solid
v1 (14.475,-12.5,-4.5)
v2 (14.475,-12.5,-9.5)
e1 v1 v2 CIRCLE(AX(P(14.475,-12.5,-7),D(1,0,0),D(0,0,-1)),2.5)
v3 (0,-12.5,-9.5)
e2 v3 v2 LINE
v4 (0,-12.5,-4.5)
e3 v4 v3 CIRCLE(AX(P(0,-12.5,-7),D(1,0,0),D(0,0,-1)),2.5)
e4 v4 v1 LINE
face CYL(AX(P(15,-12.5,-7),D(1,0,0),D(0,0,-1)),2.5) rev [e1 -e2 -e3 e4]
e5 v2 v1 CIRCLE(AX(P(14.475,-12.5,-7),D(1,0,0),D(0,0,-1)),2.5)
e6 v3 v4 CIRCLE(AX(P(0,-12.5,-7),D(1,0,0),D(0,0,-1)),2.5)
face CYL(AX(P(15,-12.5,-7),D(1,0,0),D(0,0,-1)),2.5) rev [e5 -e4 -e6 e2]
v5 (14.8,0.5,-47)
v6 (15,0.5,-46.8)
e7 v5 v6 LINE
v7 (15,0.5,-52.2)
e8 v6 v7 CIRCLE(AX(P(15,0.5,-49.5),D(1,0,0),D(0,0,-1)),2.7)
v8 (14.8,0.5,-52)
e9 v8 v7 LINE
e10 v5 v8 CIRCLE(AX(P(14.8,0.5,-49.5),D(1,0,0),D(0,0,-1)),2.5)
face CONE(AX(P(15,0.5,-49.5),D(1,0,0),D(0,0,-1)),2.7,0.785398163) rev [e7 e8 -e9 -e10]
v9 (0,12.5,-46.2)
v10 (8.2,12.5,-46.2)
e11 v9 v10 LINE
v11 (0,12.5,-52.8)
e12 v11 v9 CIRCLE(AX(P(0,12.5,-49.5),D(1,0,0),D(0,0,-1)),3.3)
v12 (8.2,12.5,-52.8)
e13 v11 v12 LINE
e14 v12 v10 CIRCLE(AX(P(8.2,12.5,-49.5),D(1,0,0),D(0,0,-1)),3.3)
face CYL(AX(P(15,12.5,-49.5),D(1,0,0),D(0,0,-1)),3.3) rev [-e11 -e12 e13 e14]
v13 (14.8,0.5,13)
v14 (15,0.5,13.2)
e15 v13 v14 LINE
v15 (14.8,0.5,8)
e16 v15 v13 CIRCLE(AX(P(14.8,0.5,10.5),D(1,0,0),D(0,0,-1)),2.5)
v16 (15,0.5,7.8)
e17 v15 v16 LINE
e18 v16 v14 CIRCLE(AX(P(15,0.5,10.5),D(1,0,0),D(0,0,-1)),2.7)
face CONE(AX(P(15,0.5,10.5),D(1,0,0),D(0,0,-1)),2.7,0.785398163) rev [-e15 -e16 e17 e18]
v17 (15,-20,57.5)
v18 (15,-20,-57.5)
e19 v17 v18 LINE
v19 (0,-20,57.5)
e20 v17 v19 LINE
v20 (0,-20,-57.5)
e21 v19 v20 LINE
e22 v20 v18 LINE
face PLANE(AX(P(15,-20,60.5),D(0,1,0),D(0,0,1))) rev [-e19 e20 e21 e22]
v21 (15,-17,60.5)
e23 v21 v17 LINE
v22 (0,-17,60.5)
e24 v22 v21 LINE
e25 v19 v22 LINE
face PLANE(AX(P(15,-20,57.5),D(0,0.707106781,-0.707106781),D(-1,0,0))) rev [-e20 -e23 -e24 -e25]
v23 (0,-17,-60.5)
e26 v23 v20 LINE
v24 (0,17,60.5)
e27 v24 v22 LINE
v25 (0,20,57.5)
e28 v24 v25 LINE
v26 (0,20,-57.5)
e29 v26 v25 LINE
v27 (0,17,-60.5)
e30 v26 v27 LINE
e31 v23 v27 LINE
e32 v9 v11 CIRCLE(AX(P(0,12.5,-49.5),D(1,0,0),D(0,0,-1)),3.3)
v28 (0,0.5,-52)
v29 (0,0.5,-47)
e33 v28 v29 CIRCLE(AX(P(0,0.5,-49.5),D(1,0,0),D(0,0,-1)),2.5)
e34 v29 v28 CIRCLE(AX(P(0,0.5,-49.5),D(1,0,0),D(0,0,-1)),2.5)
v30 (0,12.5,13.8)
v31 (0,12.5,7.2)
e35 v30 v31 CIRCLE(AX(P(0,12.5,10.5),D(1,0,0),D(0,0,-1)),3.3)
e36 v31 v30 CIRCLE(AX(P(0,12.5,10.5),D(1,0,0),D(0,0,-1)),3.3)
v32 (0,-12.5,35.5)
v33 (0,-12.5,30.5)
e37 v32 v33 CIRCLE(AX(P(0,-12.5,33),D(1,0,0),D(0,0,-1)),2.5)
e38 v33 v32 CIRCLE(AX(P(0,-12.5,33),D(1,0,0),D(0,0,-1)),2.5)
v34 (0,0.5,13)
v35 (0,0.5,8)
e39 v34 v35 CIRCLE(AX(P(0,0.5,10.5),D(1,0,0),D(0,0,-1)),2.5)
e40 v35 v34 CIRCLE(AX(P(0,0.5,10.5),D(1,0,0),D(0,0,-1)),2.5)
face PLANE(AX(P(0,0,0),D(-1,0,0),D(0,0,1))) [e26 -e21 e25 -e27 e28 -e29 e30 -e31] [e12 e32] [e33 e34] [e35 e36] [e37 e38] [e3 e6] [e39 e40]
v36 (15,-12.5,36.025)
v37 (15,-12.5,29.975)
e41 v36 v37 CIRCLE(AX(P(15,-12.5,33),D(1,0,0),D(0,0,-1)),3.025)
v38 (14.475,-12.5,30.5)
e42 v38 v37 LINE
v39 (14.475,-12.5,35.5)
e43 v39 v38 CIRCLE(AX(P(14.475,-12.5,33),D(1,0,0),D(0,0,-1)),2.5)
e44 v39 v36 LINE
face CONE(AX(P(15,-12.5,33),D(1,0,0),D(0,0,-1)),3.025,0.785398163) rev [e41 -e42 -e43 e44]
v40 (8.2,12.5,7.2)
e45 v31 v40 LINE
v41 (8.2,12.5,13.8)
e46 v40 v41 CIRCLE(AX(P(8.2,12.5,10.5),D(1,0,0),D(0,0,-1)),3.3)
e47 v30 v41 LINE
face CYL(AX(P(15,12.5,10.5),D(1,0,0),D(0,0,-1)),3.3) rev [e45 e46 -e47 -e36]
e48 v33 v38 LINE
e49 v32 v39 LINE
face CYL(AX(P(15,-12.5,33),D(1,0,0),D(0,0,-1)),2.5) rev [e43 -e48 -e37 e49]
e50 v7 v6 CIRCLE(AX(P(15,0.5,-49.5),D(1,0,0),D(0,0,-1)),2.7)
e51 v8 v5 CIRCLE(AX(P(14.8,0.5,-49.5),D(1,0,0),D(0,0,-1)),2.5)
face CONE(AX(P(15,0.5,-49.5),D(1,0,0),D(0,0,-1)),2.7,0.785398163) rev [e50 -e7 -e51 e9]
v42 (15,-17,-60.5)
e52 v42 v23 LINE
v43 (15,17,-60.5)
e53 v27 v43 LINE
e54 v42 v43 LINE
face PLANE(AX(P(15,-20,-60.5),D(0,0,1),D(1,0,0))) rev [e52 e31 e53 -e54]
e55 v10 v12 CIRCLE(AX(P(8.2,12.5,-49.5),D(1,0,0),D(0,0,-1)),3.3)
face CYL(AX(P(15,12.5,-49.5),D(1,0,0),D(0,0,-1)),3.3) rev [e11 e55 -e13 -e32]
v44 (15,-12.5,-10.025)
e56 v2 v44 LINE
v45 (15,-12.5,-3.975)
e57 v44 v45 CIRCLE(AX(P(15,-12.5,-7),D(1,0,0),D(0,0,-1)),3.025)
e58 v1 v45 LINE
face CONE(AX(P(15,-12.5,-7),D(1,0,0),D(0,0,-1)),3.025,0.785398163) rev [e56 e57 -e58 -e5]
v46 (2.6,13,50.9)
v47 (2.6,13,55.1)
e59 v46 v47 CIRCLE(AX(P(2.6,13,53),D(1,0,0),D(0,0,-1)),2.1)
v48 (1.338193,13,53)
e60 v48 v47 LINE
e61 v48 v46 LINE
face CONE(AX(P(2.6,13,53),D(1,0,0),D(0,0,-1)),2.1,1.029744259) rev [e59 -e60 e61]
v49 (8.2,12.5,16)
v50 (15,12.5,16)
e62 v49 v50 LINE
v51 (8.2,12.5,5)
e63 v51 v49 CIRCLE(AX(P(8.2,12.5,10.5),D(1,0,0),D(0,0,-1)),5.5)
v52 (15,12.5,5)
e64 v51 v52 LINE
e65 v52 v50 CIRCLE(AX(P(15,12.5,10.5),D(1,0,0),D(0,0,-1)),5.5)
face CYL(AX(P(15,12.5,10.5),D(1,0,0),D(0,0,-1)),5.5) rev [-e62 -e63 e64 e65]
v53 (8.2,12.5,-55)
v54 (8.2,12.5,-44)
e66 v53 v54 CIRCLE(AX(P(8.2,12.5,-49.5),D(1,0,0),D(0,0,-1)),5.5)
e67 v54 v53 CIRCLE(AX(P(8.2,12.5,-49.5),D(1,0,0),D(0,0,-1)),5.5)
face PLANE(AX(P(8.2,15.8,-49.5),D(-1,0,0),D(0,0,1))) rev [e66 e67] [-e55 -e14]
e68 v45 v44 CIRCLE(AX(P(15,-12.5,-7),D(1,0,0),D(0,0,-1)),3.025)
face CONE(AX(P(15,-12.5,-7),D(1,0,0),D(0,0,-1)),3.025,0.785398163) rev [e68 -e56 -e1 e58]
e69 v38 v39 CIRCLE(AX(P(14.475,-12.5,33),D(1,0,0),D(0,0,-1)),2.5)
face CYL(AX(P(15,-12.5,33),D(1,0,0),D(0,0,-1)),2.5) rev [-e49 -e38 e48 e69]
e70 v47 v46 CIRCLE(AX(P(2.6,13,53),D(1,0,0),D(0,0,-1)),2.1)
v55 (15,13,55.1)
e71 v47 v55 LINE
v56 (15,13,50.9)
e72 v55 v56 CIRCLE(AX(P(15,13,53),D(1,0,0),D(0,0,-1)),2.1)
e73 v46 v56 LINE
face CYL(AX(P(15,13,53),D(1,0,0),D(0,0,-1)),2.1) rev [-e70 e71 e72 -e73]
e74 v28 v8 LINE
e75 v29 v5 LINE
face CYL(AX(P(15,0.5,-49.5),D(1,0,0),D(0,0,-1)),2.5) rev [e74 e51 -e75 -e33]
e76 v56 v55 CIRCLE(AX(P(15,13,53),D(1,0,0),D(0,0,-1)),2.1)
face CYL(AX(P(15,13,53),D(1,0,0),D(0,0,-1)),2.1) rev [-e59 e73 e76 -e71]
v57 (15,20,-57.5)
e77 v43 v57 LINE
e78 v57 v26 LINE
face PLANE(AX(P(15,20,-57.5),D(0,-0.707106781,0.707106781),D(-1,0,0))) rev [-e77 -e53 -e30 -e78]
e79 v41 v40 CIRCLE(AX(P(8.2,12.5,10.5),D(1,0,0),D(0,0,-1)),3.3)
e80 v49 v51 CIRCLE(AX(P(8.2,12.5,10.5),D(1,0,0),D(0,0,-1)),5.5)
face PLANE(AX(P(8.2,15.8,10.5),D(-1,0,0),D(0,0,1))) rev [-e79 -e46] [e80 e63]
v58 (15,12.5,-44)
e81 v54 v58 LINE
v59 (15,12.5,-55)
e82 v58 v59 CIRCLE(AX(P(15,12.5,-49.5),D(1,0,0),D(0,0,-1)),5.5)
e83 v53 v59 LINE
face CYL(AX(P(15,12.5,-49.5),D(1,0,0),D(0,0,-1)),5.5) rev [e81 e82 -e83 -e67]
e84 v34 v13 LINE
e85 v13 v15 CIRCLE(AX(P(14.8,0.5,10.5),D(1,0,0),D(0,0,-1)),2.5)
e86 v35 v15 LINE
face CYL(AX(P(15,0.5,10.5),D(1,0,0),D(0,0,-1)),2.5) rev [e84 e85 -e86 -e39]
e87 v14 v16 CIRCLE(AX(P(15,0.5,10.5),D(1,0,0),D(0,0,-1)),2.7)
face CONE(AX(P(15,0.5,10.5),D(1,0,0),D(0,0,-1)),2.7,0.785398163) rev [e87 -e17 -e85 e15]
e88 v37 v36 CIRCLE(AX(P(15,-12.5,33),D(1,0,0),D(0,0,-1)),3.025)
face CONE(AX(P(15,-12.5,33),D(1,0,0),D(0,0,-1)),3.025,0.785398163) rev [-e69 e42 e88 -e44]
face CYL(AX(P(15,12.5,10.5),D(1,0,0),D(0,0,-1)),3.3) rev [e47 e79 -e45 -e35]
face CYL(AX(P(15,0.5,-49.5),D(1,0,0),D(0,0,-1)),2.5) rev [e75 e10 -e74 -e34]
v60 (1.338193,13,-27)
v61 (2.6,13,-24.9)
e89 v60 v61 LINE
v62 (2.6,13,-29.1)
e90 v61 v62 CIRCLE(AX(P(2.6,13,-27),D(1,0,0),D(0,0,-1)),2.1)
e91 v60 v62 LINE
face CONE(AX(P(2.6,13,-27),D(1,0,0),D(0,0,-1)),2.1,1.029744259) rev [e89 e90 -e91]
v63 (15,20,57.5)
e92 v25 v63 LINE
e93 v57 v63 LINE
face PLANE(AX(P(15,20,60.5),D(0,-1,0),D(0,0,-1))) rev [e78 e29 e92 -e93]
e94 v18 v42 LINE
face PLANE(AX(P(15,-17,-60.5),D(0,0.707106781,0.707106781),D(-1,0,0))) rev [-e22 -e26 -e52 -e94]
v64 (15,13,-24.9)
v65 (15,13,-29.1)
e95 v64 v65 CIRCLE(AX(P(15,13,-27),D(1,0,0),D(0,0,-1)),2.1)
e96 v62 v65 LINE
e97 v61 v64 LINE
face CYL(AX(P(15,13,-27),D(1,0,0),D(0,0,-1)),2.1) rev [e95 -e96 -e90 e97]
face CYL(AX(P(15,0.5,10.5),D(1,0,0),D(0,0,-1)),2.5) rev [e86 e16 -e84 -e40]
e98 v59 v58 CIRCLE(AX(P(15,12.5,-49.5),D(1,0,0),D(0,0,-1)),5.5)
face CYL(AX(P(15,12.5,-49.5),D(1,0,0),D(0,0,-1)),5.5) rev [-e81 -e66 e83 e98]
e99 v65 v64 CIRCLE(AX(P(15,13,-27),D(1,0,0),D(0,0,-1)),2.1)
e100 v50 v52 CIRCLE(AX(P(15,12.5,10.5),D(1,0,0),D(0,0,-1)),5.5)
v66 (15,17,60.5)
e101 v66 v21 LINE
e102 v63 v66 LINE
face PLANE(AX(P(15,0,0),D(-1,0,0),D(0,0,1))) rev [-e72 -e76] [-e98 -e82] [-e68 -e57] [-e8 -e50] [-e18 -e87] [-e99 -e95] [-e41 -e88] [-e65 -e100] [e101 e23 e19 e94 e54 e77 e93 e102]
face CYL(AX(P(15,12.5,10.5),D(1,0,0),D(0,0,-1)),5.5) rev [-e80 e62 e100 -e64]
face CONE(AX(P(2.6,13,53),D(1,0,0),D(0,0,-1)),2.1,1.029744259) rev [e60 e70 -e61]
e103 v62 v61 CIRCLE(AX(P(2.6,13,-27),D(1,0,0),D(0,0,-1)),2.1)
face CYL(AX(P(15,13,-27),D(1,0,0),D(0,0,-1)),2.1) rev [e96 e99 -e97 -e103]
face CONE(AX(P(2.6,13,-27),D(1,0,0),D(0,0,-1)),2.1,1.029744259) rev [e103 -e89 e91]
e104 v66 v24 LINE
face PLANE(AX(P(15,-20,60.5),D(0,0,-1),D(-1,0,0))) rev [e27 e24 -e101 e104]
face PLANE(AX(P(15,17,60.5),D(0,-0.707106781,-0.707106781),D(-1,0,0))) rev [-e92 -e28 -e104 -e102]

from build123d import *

# Parameters (mm, degrees)
SKETCH1_W                                            = 121
SKETCH1_H                                            = 40
BOSS_EXTRUDE1_DEPTH                                  = 15
M5_TAPPED_HOLE1_D                                    = 4.2
M5_TAPPED_HOLE1_DEPTH                                = 12.4
M5_TAPPED_HOLE1_TIP                                  = 1.2618073
M6_TAPPED_HOLE1_D                                    = 5
M6_TAPPED_HOLE1_DEPTH                                = 15
M6_TAPPED_HOLE1_CSINK_D                              = 6.05
M6_TAPPED_HOLE1_CSINK_ANGLE                          = 90
M6_TAPPED_HOLE1_TIP                                  = 1.502151548
CBORE_FOR_M6_HEXAGON_SOCKET_HEAD_CAP_SCR_D           = 6.6
CBORE_FOR_M6_HEXAGON_SOCKET_HEAD_CAP_SCR_CBORE_D     = 11
CBORE_FOR_M6_HEXAGON_SOCKET_HEAD_CAP_SCR_CBORE_DEPTH = 6.8
F_5_0MM_BLIND_HOLE_1_D                               = 5
F_5_0MM_BLIND_HOLE_1_CSINK_D                         = 5.4
F_5_0MM_BLIND_HOLE_1_CSINK_ANGLE                     = 90
CHAMFER1_SIZE                                        = 3


with BuildPart() as part:
    # Sketch1 → Boss-Extrude1 (new body)
    with BuildSketch(Plane(origin=(0, 0, 0), x_dir=(0, 0, -1), z_dir=(1, 0, 0))):
        Rectangle(SKETCH1_W, SKETCH1_H)
    extrude(amount=BOSS_EXTRUDE1_DEPTH)

    # M5 Tapped Hole1
    with Locations(Plane(origin=(15, 0, 0), x_dir=(0, 0, -1), z_dir=(1, 0, 0))):
        with Locations((-53, 13), (27, 13)):
            Hole(M5_TAPPED_HOLE1_D / 2, depth=M5_TAPPED_HOLE1_DEPTH)
            with Locations((0, 0, -(M5_TAPPED_HOLE1_DEPTH + M5_TAPPED_HOLE1_TIP / 2))):  # 118° drill point
                Cone(0, M5_TAPPED_HOLE1_D / 2, M5_TAPPED_HOLE1_TIP, mode=Mode.SUBTRACT)

    # M6 Tapped Hole1
    with Locations(Plane(origin=(15, 0, 0), x_dir=(0, 0, -1), z_dir=(1, 0, 0))):
        with Locations((-33, -12.5), (7, -12.5)):
            CounterSinkHole(M6_TAPPED_HOLE1_D / 2, M6_TAPPED_HOLE1_CSINK_D / 2, depth=M6_TAPPED_HOLE1_DEPTH, counter_sink_angle=M6_TAPPED_HOLE1_CSINK_ANGLE)
            with Locations((0, 0, -(M6_TAPPED_HOLE1_DEPTH + M6_TAPPED_HOLE1_TIP / 2))):  # 118° drill point
                Cone(0, M6_TAPPED_HOLE1_D / 2, M6_TAPPED_HOLE1_TIP, mode=Mode.SUBTRACT)

    # CBORE for M6 Hexagon socket head cap screws1 (through all)
    with Locations(Plane(origin=(15, 0, 0), x_dir=(0, 0, -1), z_dir=(1, 0, 0))):
        with Locations((-10.5, 12.5), (49.5, 12.5)):
            CounterBoreHole(CBORE_FOR_M6_HEXAGON_SOCKET_HEAD_CAP_SCR_D / 2, CBORE_FOR_M6_HEXAGON_SOCKET_HEAD_CAP_SCR_CBORE_D / 2, CBORE_FOR_M6_HEXAGON_SOCKET_HEAD_CAP_SCR_CBORE_DEPTH)

    # Ø5.0mm blind hole 1 (through all)
    with Locations(Plane(origin=(15, 0, 0), x_dir=(0, 0, -1), z_dir=(1, 0, 0))):
        with Locations((-10.5, 0.5), (49.5, 0.5)):
            CounterSinkHole(F_5_0MM_BLIND_HOLE_1_D / 2, F_5_0MM_BLIND_HOLE_1_CSINK_D / 2, counter_sink_angle=F_5_0MM_BLIND_HOLE_1_CSINK_ANGLE)

    # Chamfer1
    chamfer1_edges = [part.edges().sort_by_distance(p)[0] for p in [
        (7.5, -20, -60.5),
        (7.5, -20, 60.5),
        (7.5, 20, 60.5),
        (7.5, 20, -60.5),
    ]]
    chamfer(chamfer1_edges, length=CHAMFER1_SIZE)


solid = part.part
